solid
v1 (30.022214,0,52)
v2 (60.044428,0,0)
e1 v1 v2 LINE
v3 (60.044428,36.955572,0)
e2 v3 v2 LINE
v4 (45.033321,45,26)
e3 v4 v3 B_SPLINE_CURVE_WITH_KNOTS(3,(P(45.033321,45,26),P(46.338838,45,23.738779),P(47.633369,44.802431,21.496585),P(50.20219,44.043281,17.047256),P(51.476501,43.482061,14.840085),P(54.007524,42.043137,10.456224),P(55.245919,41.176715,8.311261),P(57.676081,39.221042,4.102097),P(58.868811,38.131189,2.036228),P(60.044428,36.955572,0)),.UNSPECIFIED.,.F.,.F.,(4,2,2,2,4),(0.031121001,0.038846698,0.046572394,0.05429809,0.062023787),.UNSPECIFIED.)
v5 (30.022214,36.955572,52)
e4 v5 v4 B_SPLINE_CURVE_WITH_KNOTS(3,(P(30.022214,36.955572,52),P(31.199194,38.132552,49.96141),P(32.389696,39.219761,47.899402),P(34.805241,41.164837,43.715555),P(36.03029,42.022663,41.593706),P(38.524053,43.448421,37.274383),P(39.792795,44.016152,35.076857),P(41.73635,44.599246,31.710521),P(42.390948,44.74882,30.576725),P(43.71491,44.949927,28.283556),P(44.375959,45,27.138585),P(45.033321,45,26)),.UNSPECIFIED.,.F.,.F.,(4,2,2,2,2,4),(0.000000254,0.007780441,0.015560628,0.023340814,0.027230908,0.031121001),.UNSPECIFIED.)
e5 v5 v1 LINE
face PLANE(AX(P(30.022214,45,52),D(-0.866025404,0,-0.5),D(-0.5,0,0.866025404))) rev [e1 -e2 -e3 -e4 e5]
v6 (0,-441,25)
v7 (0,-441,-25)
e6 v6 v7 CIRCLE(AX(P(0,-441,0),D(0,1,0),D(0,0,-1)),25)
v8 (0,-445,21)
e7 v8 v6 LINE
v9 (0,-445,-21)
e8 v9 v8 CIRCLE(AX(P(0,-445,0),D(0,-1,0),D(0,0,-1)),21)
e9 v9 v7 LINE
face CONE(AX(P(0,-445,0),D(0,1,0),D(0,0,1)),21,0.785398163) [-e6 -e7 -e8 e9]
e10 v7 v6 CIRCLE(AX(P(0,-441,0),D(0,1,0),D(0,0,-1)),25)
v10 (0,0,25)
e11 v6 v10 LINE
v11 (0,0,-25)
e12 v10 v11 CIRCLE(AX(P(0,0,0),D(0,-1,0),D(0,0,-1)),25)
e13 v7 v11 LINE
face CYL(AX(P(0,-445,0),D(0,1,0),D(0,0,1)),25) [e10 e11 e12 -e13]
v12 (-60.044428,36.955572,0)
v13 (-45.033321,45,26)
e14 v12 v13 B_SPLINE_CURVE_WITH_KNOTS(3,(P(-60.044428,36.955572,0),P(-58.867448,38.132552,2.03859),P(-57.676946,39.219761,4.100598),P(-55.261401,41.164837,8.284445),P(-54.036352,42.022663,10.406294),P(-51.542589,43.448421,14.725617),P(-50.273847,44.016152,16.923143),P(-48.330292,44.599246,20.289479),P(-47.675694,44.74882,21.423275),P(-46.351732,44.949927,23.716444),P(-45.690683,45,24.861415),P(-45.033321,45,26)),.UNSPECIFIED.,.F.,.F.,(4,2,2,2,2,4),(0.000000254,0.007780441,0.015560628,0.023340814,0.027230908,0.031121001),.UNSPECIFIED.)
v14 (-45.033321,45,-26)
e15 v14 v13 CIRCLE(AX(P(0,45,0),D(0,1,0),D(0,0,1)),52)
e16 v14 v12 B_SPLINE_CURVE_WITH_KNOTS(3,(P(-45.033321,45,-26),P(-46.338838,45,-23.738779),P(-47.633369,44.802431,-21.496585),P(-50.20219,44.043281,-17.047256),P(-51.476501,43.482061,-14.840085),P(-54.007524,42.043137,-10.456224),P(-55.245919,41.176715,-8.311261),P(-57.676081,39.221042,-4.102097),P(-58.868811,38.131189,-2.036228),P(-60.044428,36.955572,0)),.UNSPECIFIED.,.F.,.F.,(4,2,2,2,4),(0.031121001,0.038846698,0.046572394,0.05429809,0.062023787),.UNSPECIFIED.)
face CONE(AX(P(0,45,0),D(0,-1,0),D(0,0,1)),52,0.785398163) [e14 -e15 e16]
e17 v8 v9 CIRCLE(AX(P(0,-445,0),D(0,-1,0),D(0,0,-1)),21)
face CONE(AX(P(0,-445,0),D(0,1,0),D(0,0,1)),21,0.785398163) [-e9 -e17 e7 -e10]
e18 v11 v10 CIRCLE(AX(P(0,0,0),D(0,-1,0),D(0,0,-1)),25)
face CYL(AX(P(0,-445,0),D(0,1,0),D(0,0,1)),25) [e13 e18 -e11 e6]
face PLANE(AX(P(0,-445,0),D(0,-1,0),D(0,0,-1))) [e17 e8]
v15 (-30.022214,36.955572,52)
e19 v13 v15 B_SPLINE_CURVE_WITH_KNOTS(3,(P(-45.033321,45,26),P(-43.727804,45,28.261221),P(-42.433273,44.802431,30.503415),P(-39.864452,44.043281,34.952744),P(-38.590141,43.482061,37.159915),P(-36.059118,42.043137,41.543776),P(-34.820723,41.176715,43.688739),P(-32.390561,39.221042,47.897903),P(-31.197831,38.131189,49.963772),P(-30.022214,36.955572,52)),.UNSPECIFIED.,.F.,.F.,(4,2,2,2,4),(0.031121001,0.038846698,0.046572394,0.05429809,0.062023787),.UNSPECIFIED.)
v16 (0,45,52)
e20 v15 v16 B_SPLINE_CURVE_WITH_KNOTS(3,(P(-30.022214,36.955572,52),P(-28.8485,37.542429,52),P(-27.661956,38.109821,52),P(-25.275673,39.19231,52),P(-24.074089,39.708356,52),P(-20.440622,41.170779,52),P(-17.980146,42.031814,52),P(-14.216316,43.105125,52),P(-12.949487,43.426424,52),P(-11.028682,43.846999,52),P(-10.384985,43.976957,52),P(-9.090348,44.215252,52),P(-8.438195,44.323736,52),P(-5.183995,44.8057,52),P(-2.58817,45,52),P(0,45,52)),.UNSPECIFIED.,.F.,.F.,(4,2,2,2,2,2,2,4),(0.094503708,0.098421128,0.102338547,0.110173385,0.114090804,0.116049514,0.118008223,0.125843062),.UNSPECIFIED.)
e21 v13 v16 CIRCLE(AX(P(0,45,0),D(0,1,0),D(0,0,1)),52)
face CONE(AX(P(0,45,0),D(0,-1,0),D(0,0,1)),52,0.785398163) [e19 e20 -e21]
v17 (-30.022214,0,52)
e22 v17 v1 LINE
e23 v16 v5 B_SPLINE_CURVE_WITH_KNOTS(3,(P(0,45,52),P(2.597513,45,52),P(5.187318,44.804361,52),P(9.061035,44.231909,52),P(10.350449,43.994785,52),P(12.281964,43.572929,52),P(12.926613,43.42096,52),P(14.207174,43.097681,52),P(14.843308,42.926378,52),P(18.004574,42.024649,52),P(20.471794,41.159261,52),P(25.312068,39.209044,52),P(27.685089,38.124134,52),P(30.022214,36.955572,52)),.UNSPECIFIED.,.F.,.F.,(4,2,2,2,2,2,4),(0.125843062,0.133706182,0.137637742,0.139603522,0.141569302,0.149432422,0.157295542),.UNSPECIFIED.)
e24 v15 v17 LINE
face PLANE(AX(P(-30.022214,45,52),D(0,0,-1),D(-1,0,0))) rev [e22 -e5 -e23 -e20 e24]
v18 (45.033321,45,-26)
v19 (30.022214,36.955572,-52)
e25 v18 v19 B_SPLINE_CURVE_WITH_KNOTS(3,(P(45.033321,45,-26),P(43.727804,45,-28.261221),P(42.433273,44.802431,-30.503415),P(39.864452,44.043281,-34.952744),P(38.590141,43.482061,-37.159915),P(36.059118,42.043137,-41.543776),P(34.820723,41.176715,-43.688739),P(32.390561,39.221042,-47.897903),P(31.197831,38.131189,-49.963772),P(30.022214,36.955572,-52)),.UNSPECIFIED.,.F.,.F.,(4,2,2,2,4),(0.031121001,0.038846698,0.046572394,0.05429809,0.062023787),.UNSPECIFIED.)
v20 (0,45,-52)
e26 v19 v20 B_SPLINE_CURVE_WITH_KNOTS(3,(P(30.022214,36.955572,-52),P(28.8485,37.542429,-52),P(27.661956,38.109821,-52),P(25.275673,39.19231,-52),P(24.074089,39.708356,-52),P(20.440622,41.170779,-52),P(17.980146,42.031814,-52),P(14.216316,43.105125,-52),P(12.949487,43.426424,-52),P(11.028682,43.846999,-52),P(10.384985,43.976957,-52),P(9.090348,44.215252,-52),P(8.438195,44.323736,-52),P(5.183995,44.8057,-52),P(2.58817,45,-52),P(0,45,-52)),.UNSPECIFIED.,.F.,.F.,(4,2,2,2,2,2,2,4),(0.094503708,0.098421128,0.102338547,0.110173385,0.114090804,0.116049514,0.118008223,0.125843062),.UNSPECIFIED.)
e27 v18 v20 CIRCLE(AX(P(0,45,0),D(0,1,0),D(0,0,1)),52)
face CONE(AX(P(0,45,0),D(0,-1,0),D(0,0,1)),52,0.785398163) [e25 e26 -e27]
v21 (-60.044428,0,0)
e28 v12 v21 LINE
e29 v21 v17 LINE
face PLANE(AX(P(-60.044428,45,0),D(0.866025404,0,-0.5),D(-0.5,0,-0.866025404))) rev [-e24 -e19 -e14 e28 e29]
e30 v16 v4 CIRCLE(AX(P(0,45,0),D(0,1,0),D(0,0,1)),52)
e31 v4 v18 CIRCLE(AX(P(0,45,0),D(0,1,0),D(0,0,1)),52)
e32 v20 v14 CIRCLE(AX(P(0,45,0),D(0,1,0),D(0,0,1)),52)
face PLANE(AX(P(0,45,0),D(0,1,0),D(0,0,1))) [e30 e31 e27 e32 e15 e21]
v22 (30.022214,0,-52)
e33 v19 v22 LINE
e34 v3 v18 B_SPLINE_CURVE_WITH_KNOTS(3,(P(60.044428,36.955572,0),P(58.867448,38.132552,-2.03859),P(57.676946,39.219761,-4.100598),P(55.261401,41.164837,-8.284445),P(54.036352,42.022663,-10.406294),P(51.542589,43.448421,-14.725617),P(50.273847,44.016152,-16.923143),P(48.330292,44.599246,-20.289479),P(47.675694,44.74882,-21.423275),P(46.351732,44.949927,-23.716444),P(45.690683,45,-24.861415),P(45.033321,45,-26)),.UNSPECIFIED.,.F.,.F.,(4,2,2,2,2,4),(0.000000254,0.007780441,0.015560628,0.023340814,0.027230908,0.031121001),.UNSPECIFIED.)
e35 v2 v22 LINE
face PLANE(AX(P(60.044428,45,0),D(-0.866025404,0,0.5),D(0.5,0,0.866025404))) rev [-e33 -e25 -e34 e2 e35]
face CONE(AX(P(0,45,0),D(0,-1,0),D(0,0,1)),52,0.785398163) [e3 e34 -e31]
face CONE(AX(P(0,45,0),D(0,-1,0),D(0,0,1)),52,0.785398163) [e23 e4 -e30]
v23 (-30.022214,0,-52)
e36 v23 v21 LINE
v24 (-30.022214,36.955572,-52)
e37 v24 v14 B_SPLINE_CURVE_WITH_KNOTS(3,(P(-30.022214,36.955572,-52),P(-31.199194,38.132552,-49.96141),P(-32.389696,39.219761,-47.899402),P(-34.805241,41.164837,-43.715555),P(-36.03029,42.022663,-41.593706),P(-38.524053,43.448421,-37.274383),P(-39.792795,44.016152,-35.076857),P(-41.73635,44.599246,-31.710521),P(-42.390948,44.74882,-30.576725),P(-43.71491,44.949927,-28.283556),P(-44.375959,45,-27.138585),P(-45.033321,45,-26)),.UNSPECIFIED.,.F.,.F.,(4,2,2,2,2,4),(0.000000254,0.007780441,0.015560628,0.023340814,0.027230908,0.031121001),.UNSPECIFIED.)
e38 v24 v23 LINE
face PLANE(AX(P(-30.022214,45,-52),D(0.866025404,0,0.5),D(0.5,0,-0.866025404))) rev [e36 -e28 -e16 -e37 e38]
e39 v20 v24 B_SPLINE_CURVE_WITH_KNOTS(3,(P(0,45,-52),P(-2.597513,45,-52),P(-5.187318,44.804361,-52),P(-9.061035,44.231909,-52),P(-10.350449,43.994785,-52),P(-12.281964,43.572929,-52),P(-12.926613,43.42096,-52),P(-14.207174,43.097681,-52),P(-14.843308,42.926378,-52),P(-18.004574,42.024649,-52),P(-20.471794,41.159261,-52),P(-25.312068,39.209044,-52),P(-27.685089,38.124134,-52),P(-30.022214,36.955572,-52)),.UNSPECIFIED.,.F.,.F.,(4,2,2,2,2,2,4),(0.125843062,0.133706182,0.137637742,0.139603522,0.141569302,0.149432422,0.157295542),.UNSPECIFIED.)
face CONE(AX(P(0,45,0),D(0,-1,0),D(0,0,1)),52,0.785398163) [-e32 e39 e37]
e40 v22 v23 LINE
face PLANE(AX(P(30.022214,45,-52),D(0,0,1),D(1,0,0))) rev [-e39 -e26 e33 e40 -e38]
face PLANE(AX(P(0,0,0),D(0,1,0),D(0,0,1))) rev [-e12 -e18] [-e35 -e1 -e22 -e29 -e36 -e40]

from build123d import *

# Parameters (mm, degrees)
HEX_HEAD_DEPTH                 = 45
HEAD_CHAMFER_PROFILE_OUTSIDE_W = 245.11
HEAD_CHAMFER_PROFILE_OUTSIDE_H = 229.022
HEAD_CHAMFER_PROFILE_OUTSIDE_R = 52
HEAD_TOP_CHAMFER_45DEG_DEPTH   = 45
HEAD_TOP_CHAMFER_45DEG_DRAFT   = -45
SHANK_PROFILE_50_R             = 25
SHANK_50X445_DEPTH             = 445
SHANK_END_CHAMFER_4X45DEG_SIZE = 4


with BuildPart() as part:
    # Hex Head Profile 104AF → Hex Head (new body)
    with BuildSketch(Plane(origin=(0, 0, 0), x_dir=(1, 0, 0), z_dir=(0, 1, 0))):
        Polygon((30.022213998, -52), (60.044427996, 0), (30.022213998, 52), (-30.022213998, 52), (-60.044427996, 0), (-30.022213998, -52), align=None)
    extrude(amount=HEX_HEAD_DEPTH)


with BuildPart() as head_top_chamfer_45deg_tool:
    # Head Chamfer Profile outside → Head Top Chamfer 45deg (with draft: the straight prism first)
    with BuildSketch(Plane(origin=(0, 45, 0), x_dir=(1, 0, 0), z_dir=(0, 1, 0))):
        Rectangle(HEAD_CHAMFER_PROFILE_OUTSIDE_W, HEAD_CHAMFER_PROFILE_OUTSIDE_H)
        Circle(HEAD_CHAMFER_PROFILE_OUTSIDE_R, mode=Mode.SUBTRACT)
    extrude(amount=-HEAD_TOP_CHAMFER_45DEG_DEPTH)
    # Head Top Chamfer 45deg: the draft: its side faces are tilted about the plane it starts from
    head_top_chamfer_45deg_sides = [head_top_chamfer_45deg_tool.faces().sort_by_distance(p)[0] for p in [
        (0, 22.5, 114.511),
        (122.555, 22.5, 0),
        (0, 22.5, -114.511),
        (-122.555, 22.5, 0),
        (-52, 22.5, 0),
    ]]
    draft(head_top_chamfer_45deg_sides, Plane(origin=(0, 45, 0), x_dir=(1, 0, 0), z_dir=(0, 1, 0)), HEAD_TOP_CHAMFER_45DEG_DRAFT)


with BuildPart() as part_1:
    add(part.part)

    # Head Top Chamfer 45deg: cut by head_top_chamfer_45deg_tool
    add(head_top_chamfer_45deg_tool.part, mode=Mode.SUBTRACT)

    # Shank Profile Ø50 → Shank Ø50x445 (add)
    with BuildSketch(Plane.XZ):
        with Locations(Location((0, 0, 0), (0, 0, 270))):
            Circle(SHANK_PROFILE_50_R)
    extrude(amount=SHANK_50X445_DEPTH)

    # Shank End Chamfer 4x45deg
    shank_end_chamfer_4x45deg_edges = [part_1.edges().sort_by_distance(p)[0] for p in [
        (0, -445, 25),
    ]]
    chamfer(shank_end_chamfer_4x45deg_edges, length=SHANK_END_CHAMFER_4X45DEG_SIZE)


solid = part_1.part
